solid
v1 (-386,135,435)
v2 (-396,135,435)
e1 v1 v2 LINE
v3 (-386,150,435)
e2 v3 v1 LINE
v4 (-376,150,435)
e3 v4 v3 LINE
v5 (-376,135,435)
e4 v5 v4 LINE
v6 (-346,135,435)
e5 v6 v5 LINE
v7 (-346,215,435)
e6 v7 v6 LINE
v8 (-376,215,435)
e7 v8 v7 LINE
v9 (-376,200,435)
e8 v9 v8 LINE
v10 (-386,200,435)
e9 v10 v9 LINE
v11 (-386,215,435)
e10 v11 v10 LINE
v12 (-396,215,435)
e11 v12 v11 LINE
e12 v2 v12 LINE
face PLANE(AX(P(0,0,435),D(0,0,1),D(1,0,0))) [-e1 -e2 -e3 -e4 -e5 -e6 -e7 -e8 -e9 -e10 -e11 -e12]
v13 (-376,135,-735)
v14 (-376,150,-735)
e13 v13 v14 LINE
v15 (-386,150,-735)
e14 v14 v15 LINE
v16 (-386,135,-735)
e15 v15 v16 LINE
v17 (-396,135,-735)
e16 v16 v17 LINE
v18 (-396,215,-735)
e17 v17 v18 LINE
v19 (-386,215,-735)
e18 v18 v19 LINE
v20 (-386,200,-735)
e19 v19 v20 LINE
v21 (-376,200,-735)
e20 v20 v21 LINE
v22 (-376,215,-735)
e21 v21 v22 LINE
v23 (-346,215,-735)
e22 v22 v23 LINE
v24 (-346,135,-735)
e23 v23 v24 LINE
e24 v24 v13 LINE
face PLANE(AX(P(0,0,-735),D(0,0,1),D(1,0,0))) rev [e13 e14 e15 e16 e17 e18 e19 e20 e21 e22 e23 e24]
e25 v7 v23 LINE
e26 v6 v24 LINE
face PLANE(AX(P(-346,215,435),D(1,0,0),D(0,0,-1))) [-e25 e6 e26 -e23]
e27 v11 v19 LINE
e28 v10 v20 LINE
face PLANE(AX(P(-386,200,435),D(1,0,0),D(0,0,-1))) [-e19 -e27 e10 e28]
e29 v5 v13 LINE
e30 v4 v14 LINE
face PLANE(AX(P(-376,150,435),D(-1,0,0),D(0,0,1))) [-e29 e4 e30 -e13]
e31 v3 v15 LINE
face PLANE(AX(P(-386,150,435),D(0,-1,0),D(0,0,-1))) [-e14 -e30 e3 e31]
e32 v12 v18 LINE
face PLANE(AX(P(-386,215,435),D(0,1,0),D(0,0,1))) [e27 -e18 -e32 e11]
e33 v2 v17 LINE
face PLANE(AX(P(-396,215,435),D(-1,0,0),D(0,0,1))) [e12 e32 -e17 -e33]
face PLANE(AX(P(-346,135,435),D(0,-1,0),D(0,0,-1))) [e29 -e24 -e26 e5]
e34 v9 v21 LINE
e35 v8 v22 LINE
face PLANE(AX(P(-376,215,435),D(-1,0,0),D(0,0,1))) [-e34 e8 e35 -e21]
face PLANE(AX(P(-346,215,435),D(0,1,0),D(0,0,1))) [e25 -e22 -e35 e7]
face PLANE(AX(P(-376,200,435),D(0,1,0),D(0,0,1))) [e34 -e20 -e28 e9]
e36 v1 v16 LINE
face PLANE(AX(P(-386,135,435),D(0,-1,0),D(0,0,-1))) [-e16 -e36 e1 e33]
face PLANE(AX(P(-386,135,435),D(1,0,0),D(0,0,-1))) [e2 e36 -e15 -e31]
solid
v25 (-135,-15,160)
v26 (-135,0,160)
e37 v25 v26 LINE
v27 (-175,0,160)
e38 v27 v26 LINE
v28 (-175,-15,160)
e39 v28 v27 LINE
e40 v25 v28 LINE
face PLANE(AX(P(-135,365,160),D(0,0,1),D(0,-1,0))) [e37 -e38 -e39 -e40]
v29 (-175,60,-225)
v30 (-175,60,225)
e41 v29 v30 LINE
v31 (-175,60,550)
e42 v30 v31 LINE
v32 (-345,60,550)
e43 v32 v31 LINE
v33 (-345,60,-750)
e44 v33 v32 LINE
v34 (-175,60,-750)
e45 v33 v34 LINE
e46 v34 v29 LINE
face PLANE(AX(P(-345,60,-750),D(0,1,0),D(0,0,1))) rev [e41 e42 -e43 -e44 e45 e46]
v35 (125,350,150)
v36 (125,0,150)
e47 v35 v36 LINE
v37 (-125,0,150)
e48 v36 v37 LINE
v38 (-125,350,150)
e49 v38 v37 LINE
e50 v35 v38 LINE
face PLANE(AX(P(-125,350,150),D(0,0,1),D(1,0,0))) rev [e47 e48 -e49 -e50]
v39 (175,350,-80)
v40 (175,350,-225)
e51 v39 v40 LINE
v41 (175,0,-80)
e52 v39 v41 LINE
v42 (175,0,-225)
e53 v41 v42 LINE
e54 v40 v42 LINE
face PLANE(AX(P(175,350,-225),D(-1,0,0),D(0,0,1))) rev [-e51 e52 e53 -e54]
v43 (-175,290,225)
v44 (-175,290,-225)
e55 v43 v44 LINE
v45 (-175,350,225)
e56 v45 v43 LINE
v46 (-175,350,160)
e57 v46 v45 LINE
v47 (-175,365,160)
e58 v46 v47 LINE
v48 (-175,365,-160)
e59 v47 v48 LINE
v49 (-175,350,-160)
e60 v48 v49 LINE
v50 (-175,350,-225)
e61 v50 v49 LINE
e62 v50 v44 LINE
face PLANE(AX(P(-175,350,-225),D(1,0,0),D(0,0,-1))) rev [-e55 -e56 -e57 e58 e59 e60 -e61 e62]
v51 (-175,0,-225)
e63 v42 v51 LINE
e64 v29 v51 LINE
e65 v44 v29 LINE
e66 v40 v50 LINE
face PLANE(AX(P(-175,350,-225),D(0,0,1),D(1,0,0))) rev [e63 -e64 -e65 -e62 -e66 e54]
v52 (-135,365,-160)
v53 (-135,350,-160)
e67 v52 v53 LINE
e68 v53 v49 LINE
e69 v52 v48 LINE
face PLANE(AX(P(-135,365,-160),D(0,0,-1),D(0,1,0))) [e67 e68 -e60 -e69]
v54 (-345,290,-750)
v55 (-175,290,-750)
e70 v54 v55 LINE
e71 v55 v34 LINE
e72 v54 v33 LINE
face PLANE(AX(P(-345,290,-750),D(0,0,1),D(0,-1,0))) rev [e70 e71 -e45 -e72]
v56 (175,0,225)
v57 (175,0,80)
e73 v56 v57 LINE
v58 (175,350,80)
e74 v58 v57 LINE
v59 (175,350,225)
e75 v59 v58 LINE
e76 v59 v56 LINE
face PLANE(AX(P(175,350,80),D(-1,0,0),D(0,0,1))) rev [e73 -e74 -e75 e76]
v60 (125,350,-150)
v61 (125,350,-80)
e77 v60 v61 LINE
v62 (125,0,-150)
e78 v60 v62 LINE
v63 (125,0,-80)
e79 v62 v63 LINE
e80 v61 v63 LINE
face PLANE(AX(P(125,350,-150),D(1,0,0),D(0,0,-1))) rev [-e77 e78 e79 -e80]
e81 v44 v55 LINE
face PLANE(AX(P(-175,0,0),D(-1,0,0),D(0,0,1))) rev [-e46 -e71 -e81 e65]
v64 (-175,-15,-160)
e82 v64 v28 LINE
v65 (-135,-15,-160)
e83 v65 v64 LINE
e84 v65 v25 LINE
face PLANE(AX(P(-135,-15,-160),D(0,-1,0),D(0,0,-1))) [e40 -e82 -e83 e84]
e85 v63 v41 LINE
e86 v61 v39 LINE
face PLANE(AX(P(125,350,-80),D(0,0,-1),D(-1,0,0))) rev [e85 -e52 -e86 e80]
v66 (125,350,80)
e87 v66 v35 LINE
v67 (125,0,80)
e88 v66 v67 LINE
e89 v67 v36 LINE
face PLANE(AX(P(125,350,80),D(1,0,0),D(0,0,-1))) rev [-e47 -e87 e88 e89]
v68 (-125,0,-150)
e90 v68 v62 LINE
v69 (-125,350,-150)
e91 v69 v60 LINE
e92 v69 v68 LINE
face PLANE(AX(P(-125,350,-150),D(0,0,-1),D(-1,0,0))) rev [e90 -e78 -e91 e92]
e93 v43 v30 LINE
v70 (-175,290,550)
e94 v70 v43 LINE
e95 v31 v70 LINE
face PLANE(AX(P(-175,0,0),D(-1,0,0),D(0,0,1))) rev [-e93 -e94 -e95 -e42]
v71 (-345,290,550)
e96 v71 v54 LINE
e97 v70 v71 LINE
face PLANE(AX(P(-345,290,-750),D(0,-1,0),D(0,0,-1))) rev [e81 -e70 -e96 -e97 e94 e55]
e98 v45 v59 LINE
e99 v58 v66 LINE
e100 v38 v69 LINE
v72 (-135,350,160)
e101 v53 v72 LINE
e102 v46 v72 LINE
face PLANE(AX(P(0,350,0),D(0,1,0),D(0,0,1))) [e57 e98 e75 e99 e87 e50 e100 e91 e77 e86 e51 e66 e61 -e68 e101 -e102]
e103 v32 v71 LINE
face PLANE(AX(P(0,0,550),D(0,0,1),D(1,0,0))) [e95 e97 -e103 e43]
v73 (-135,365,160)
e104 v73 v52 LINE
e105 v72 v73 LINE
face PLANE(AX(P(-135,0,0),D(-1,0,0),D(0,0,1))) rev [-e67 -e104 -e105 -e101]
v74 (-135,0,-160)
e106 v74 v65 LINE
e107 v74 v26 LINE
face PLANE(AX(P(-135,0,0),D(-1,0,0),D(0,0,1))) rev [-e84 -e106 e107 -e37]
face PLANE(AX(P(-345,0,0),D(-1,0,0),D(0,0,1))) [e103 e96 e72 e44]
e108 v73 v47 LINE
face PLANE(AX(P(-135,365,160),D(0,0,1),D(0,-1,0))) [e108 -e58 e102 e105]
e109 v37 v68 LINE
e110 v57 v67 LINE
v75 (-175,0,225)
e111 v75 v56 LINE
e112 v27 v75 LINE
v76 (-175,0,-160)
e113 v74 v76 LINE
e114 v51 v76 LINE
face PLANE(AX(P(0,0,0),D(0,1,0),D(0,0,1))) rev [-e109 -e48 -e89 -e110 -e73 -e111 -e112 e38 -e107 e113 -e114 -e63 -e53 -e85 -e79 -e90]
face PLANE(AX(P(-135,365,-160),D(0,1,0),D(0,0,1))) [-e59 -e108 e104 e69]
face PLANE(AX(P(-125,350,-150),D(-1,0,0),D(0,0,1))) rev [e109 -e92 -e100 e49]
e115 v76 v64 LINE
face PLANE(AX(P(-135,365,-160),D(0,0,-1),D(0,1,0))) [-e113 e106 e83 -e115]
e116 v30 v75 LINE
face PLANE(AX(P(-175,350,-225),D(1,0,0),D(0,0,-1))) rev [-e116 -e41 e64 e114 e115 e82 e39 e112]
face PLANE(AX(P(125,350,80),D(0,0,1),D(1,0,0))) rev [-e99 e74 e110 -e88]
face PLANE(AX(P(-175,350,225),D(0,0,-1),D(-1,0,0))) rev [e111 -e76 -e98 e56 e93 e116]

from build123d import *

# Parameters (mm, degrees)
BOSS_EXTRUDE1_DEPTH = 350
SKETCH2_W           = 320
SKETCH2_H           = 380
BOSS_EXTRUDE2_DEPTH = 40
SKETCH3_W           = 1500
SKETCH3_H           = 230
BOSS_EXTRUDE3_DEPTH = 170
SKETCH5_W           = 220.101814103
SKETCH5_H           = 309.079143209
CUT_EXTRUDE2_DEPTH  = 200
BOSS_EXTRUDE4_DEPTH = 1170


with BuildPart() as part:
    # Sketch1 → Boss-Extrude1 (new body)
    with BuildSketch(Plane(origin=(0, 0, 0), x_dir=(1, 0, 0), z_dir=(0, 1, 0))):
        Polygon((125, 80), (175, 80), (175, 225), (-175, 225), (-175, -225), (175, -225), (175, -80), (125, -80), (125, -150), (-125, -150), (-125, 150), (125, 150), align=None)
    extrude(amount=BOSS_EXTRUDE1_DEPTH)

    # Sketch2 → Boss-Extrude2 (add)
    with BuildSketch(Plane.ZY.offset(175)):
        with Locations((0, 175)):
            Rectangle(SKETCH2_W, SKETCH2_H)
    extrude(amount=-BOSS_EXTRUDE2_DEPTH)

    # Sketch3 → Boss-Extrude3 (add)
    with BuildSketch(Plane.ZY.offset(175)):
        with Locations((0, 175)):
            Rectangle(SKETCH3_W, SKETCH3_H)
    extrude(amount=BOSS_EXTRUDE3_DEPTH)

    # Sketch5 → Cut-Extrude2 (cut)
    with BuildSketch(Plane.XY.offset(750)):
        with Locations((-250.36904916, 177.341508661)):
            Rectangle(SKETCH5_W, SKETCH5_H)
    extrude(amount=-CUT_EXTRUDE2_DEPTH, mode=Mode.SUBTRACT)


with BuildPart() as body_2:
    # Sketch6 → Boss-Extrude4 (new body)
    with BuildSketch(Plane(origin=(0, 0, -735), x_dir=(-1, 0, 0), z_dir=(0, 0, -1))):
        Polygon((346, 215), (376, 215), (376, 200), (386, 200), (386, 215), (396, 215), (396, 135), (386, 135), (386, 150), (376, 150), (376, 135), (346, 135), align=None)
    extrude(amount=-BOSS_EXTRUDE4_DEPTH)


solid = Compound([part.part, body_2.part])
